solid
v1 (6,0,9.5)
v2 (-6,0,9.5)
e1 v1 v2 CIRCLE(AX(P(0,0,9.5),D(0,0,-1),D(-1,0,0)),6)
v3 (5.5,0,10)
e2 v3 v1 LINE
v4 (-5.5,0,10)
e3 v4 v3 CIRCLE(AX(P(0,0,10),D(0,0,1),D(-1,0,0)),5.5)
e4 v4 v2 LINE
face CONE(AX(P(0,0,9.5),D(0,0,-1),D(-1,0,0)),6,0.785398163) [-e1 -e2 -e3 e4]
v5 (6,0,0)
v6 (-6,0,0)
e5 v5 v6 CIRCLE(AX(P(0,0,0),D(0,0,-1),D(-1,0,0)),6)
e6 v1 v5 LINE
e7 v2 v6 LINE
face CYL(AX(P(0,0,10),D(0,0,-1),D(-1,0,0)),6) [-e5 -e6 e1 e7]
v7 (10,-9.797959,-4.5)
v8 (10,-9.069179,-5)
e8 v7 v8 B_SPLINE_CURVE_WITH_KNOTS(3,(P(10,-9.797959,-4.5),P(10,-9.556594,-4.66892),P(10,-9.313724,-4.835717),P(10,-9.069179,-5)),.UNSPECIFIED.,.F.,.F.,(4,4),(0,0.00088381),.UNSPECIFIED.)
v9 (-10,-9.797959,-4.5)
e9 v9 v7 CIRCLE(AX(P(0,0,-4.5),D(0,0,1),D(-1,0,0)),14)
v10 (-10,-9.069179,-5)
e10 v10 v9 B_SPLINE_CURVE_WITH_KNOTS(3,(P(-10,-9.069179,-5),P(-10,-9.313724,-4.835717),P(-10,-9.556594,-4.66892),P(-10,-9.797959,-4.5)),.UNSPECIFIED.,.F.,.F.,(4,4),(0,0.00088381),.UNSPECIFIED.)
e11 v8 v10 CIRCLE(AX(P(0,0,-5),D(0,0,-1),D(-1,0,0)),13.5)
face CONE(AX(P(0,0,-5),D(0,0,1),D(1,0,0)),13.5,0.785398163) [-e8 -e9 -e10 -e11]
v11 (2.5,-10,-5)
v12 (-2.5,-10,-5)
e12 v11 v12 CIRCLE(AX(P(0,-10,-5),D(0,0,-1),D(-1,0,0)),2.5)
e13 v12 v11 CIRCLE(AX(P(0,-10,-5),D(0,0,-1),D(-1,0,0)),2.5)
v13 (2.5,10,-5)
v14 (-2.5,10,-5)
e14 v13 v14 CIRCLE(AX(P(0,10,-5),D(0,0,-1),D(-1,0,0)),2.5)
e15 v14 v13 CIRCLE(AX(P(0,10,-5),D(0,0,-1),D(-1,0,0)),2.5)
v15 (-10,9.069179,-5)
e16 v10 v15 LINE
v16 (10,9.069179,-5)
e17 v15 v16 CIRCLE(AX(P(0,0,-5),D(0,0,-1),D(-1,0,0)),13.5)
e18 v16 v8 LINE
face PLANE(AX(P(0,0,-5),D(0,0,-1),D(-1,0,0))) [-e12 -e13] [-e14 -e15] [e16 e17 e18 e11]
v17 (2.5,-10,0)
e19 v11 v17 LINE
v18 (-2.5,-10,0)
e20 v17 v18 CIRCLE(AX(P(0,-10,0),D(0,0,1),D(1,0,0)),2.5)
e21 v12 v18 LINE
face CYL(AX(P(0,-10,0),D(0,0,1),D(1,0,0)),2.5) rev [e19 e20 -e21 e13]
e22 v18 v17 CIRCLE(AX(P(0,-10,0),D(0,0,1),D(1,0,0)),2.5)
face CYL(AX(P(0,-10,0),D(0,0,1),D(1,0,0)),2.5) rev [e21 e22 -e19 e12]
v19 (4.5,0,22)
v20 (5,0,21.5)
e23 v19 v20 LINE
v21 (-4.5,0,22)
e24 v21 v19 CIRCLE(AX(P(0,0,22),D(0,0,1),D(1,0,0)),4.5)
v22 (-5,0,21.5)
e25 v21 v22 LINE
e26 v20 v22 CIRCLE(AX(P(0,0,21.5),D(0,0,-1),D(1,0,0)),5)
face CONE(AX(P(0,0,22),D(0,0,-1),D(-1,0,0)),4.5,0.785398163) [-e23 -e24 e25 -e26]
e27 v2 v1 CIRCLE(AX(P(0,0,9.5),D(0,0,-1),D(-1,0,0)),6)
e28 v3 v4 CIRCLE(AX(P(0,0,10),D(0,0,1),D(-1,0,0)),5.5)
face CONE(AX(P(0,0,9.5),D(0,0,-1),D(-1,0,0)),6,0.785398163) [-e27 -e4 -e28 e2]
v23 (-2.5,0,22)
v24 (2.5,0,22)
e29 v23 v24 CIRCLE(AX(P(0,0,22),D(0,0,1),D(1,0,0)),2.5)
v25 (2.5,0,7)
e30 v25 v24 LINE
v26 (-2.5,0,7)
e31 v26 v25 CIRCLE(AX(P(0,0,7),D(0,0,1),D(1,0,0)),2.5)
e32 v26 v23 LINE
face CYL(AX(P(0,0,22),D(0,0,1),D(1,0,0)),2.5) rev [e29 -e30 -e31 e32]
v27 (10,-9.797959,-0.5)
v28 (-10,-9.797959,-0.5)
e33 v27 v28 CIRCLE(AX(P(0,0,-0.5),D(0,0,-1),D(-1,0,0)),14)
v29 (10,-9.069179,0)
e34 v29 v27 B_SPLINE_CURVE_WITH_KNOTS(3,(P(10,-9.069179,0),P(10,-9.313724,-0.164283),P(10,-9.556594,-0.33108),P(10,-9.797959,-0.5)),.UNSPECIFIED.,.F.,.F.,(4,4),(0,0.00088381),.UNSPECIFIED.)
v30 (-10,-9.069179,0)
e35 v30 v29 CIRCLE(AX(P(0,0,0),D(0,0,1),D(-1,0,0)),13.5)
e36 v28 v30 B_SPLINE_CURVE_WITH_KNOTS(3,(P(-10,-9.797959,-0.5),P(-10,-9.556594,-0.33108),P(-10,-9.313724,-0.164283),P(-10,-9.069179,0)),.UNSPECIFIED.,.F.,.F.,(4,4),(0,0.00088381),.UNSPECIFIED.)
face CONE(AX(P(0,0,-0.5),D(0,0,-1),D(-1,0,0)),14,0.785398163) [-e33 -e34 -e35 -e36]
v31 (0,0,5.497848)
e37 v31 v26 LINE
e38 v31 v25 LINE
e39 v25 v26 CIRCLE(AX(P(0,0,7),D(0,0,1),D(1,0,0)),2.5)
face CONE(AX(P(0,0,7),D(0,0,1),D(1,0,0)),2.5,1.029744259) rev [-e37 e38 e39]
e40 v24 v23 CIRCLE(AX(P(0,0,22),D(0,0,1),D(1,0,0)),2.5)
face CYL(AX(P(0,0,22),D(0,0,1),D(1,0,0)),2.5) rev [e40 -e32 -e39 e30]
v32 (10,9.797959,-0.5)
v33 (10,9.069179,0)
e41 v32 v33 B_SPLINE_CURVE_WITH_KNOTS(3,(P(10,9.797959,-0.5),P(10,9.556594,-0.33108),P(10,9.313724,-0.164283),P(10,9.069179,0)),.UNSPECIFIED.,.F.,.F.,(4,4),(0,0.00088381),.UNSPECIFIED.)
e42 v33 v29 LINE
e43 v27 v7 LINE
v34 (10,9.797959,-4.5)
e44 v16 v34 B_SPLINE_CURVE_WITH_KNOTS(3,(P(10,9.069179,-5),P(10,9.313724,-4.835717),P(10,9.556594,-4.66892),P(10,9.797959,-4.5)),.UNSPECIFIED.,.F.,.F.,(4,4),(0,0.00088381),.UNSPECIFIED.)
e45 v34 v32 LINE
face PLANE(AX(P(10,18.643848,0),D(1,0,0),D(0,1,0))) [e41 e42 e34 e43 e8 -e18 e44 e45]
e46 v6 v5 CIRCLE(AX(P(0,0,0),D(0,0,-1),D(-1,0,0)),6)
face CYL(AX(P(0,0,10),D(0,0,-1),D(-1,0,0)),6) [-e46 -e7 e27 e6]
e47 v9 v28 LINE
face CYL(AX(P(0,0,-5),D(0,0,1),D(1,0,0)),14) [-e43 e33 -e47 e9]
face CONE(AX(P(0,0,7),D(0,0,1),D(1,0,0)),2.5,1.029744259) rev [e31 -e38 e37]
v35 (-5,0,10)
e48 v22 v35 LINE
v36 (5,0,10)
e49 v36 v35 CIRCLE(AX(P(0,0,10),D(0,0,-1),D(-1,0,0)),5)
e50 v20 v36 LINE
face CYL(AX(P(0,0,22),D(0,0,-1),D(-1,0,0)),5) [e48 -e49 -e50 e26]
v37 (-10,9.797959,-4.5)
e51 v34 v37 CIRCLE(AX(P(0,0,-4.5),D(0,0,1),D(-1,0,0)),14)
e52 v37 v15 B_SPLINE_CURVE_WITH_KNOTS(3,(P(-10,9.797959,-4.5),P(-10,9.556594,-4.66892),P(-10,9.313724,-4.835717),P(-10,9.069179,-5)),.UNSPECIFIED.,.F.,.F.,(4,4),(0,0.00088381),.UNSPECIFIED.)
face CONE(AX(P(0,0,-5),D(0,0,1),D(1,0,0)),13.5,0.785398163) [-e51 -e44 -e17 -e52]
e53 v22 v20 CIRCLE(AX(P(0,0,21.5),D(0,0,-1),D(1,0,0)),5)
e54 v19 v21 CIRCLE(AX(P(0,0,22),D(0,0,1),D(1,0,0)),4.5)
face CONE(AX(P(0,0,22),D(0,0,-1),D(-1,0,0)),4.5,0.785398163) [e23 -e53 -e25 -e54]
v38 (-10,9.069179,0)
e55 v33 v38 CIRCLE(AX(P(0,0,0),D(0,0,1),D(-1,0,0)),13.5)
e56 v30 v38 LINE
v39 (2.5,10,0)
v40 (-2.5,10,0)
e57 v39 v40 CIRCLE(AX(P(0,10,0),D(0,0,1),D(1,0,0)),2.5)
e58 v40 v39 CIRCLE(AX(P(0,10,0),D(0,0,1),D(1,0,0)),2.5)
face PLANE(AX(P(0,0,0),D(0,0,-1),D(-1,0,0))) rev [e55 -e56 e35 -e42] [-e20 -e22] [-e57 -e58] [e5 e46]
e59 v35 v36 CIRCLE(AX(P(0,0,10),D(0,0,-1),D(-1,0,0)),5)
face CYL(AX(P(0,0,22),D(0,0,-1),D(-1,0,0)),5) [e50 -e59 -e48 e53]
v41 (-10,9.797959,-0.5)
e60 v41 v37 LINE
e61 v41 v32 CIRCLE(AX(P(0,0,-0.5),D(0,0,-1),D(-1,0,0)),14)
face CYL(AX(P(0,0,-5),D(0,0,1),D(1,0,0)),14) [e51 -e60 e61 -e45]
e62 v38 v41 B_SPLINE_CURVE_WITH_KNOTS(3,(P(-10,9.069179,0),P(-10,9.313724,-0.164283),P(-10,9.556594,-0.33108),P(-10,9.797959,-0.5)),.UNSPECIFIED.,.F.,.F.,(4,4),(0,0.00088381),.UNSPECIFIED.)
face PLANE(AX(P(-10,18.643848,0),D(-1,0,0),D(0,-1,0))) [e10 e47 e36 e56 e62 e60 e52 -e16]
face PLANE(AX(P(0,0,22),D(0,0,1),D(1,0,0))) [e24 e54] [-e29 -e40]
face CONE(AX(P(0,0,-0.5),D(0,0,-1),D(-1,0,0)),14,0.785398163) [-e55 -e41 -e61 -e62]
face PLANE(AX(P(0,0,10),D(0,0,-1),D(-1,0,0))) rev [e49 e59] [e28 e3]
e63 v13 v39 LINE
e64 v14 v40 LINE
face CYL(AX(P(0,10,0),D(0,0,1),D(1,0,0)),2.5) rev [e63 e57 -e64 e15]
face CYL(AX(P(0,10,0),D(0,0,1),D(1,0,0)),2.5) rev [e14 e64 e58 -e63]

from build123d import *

# Parameters (mm, degrees)
SKETCH_1_R                = 5
EXTRUDE_1_DEPTH           = 22
SKETCH_2_R                = 6
EXTRUDE_2_DEPTH           = 10
SKETCH_3_R                = 14
EXTRUDE_3_DEPTH           = 5
SKETCH_4_OUTSIDE_W        = 39.586
SKETCH_4_OUTSIDE_H        = 39.586
SKETCH_4_OUTSIDE_W_2      = 20
SKETCH_4_OUTSIDE_H_2      = 37.741501618
CUT_EXTRUDE_1_DEPTH       = 5
HOLE_WIZARD_5_0_5_1_D     = 5
HOLE_WIZARD_5_0_5_1_DEPTH = 20
HOLE_WIZARD_5_0_5_1_TIP   = 1.502151548
HOLE_WIZARD_M6_1_D        = 5
HOLE_WIZARD_M6_1_DEPTH    = 15
HOLE_WIZARD_M6_1_TIP      = 1.502151548
CHAMFER_1_SIZE            = 0.5
CHAMFER_2_SIZE            = 0.5


with BuildPart() as part:
    # 草图1 → 凸台-拉伸1 (new body)
    with BuildSketch(Plane.XY):
        Circle(SKETCH_1_R)
    extrude(amount=EXTRUDE_1_DEPTH)

    # 草图2 → 凸台-拉伸2 (add)
    with BuildSketch(Plane(origin=(0, 0, 0), x_dir=(-1, 0, 0), z_dir=(0, 0, -1))):
        Circle(SKETCH_2_R)
    extrude(amount=-EXTRUDE_2_DEPTH)

    # 草图3 → 凸台-拉伸3 (add)
    with BuildSketch(Plane(origin=(0, 0, 0), x_dir=(-1, 0, 0), z_dir=(0, 0, -1))):
        Circle(SKETCH_3_R)
    extrude(amount=EXTRUDE_3_DEPTH)

    # 草图4 outside → 切除-拉伸1 (cut)
    with BuildSketch(Plane(origin=(0, 0, -5), x_dir=(-1, 0, 0), z_dir=(0, 0, -1))):
        Rectangle(SKETCH_4_OUTSIDE_W, SKETCH_4_OUTSIDE_H)
        with Locations((0, -0.226902815)):
            Rectangle(SKETCH_4_OUTSIDE_W_2, SKETCH_4_OUTSIDE_H_2, mode=Mode.SUBTRACT)
    extrude(amount=-CUT_EXTRUDE_1_DEPTH, mode=Mode.SUBTRACT)

    # Ø5.0 (5) 直径孔1
    with Locations(Plane.XY):
        with Locations((0, 10), (0, -10)):
            Hole(HOLE_WIZARD_5_0_5_1_D / 2, depth=HOLE_WIZARD_5_0_5_1_DEPTH)
            with Locations((0, 0, -(HOLE_WIZARD_5_0_5_1_DEPTH + HOLE_WIZARD_5_0_5_1_TIP / 2))):  # 118° drill point
                Cone(0, HOLE_WIZARD_5_0_5_1_D / 2, HOLE_WIZARD_5_0_5_1_TIP, mode=Mode.SUBTRACT)

    # M6 螺纹孔1
    with Locations(Plane.XY.offset(22)):
        with Locations((0, 0)):
            Hole(HOLE_WIZARD_M6_1_D / 2, depth=HOLE_WIZARD_M6_1_DEPTH)
            with Locations((0, 0, -(HOLE_WIZARD_M6_1_DEPTH + HOLE_WIZARD_M6_1_TIP / 2))):  # 118° drill point
                Cone(0, HOLE_WIZARD_M6_1_D / 2, HOLE_WIZARD_M6_1_TIP, mode=Mode.SUBTRACT)

    # 倒角1
    chamfer_1_edges = [part.edges().sort_by_distance(p)[0] for p in [
        (-5, 0, 22),
        (6, 0, 10),
    ]]
    chamfer(chamfer_1_edges, length=CHAMFER_1_SIZE)

    # 倒角2
    chamfer_2_edges = [part.edges().sort_by_distance(p)[0] for p in [
        (0, 14, 0),
        (0, 14, -5),
        (0, -14, 0),
        (0, -14, -5),
    ]]
    chamfer(chamfer_2_edges, length=CHAMFER_2_SIZE)


solid = part.part
